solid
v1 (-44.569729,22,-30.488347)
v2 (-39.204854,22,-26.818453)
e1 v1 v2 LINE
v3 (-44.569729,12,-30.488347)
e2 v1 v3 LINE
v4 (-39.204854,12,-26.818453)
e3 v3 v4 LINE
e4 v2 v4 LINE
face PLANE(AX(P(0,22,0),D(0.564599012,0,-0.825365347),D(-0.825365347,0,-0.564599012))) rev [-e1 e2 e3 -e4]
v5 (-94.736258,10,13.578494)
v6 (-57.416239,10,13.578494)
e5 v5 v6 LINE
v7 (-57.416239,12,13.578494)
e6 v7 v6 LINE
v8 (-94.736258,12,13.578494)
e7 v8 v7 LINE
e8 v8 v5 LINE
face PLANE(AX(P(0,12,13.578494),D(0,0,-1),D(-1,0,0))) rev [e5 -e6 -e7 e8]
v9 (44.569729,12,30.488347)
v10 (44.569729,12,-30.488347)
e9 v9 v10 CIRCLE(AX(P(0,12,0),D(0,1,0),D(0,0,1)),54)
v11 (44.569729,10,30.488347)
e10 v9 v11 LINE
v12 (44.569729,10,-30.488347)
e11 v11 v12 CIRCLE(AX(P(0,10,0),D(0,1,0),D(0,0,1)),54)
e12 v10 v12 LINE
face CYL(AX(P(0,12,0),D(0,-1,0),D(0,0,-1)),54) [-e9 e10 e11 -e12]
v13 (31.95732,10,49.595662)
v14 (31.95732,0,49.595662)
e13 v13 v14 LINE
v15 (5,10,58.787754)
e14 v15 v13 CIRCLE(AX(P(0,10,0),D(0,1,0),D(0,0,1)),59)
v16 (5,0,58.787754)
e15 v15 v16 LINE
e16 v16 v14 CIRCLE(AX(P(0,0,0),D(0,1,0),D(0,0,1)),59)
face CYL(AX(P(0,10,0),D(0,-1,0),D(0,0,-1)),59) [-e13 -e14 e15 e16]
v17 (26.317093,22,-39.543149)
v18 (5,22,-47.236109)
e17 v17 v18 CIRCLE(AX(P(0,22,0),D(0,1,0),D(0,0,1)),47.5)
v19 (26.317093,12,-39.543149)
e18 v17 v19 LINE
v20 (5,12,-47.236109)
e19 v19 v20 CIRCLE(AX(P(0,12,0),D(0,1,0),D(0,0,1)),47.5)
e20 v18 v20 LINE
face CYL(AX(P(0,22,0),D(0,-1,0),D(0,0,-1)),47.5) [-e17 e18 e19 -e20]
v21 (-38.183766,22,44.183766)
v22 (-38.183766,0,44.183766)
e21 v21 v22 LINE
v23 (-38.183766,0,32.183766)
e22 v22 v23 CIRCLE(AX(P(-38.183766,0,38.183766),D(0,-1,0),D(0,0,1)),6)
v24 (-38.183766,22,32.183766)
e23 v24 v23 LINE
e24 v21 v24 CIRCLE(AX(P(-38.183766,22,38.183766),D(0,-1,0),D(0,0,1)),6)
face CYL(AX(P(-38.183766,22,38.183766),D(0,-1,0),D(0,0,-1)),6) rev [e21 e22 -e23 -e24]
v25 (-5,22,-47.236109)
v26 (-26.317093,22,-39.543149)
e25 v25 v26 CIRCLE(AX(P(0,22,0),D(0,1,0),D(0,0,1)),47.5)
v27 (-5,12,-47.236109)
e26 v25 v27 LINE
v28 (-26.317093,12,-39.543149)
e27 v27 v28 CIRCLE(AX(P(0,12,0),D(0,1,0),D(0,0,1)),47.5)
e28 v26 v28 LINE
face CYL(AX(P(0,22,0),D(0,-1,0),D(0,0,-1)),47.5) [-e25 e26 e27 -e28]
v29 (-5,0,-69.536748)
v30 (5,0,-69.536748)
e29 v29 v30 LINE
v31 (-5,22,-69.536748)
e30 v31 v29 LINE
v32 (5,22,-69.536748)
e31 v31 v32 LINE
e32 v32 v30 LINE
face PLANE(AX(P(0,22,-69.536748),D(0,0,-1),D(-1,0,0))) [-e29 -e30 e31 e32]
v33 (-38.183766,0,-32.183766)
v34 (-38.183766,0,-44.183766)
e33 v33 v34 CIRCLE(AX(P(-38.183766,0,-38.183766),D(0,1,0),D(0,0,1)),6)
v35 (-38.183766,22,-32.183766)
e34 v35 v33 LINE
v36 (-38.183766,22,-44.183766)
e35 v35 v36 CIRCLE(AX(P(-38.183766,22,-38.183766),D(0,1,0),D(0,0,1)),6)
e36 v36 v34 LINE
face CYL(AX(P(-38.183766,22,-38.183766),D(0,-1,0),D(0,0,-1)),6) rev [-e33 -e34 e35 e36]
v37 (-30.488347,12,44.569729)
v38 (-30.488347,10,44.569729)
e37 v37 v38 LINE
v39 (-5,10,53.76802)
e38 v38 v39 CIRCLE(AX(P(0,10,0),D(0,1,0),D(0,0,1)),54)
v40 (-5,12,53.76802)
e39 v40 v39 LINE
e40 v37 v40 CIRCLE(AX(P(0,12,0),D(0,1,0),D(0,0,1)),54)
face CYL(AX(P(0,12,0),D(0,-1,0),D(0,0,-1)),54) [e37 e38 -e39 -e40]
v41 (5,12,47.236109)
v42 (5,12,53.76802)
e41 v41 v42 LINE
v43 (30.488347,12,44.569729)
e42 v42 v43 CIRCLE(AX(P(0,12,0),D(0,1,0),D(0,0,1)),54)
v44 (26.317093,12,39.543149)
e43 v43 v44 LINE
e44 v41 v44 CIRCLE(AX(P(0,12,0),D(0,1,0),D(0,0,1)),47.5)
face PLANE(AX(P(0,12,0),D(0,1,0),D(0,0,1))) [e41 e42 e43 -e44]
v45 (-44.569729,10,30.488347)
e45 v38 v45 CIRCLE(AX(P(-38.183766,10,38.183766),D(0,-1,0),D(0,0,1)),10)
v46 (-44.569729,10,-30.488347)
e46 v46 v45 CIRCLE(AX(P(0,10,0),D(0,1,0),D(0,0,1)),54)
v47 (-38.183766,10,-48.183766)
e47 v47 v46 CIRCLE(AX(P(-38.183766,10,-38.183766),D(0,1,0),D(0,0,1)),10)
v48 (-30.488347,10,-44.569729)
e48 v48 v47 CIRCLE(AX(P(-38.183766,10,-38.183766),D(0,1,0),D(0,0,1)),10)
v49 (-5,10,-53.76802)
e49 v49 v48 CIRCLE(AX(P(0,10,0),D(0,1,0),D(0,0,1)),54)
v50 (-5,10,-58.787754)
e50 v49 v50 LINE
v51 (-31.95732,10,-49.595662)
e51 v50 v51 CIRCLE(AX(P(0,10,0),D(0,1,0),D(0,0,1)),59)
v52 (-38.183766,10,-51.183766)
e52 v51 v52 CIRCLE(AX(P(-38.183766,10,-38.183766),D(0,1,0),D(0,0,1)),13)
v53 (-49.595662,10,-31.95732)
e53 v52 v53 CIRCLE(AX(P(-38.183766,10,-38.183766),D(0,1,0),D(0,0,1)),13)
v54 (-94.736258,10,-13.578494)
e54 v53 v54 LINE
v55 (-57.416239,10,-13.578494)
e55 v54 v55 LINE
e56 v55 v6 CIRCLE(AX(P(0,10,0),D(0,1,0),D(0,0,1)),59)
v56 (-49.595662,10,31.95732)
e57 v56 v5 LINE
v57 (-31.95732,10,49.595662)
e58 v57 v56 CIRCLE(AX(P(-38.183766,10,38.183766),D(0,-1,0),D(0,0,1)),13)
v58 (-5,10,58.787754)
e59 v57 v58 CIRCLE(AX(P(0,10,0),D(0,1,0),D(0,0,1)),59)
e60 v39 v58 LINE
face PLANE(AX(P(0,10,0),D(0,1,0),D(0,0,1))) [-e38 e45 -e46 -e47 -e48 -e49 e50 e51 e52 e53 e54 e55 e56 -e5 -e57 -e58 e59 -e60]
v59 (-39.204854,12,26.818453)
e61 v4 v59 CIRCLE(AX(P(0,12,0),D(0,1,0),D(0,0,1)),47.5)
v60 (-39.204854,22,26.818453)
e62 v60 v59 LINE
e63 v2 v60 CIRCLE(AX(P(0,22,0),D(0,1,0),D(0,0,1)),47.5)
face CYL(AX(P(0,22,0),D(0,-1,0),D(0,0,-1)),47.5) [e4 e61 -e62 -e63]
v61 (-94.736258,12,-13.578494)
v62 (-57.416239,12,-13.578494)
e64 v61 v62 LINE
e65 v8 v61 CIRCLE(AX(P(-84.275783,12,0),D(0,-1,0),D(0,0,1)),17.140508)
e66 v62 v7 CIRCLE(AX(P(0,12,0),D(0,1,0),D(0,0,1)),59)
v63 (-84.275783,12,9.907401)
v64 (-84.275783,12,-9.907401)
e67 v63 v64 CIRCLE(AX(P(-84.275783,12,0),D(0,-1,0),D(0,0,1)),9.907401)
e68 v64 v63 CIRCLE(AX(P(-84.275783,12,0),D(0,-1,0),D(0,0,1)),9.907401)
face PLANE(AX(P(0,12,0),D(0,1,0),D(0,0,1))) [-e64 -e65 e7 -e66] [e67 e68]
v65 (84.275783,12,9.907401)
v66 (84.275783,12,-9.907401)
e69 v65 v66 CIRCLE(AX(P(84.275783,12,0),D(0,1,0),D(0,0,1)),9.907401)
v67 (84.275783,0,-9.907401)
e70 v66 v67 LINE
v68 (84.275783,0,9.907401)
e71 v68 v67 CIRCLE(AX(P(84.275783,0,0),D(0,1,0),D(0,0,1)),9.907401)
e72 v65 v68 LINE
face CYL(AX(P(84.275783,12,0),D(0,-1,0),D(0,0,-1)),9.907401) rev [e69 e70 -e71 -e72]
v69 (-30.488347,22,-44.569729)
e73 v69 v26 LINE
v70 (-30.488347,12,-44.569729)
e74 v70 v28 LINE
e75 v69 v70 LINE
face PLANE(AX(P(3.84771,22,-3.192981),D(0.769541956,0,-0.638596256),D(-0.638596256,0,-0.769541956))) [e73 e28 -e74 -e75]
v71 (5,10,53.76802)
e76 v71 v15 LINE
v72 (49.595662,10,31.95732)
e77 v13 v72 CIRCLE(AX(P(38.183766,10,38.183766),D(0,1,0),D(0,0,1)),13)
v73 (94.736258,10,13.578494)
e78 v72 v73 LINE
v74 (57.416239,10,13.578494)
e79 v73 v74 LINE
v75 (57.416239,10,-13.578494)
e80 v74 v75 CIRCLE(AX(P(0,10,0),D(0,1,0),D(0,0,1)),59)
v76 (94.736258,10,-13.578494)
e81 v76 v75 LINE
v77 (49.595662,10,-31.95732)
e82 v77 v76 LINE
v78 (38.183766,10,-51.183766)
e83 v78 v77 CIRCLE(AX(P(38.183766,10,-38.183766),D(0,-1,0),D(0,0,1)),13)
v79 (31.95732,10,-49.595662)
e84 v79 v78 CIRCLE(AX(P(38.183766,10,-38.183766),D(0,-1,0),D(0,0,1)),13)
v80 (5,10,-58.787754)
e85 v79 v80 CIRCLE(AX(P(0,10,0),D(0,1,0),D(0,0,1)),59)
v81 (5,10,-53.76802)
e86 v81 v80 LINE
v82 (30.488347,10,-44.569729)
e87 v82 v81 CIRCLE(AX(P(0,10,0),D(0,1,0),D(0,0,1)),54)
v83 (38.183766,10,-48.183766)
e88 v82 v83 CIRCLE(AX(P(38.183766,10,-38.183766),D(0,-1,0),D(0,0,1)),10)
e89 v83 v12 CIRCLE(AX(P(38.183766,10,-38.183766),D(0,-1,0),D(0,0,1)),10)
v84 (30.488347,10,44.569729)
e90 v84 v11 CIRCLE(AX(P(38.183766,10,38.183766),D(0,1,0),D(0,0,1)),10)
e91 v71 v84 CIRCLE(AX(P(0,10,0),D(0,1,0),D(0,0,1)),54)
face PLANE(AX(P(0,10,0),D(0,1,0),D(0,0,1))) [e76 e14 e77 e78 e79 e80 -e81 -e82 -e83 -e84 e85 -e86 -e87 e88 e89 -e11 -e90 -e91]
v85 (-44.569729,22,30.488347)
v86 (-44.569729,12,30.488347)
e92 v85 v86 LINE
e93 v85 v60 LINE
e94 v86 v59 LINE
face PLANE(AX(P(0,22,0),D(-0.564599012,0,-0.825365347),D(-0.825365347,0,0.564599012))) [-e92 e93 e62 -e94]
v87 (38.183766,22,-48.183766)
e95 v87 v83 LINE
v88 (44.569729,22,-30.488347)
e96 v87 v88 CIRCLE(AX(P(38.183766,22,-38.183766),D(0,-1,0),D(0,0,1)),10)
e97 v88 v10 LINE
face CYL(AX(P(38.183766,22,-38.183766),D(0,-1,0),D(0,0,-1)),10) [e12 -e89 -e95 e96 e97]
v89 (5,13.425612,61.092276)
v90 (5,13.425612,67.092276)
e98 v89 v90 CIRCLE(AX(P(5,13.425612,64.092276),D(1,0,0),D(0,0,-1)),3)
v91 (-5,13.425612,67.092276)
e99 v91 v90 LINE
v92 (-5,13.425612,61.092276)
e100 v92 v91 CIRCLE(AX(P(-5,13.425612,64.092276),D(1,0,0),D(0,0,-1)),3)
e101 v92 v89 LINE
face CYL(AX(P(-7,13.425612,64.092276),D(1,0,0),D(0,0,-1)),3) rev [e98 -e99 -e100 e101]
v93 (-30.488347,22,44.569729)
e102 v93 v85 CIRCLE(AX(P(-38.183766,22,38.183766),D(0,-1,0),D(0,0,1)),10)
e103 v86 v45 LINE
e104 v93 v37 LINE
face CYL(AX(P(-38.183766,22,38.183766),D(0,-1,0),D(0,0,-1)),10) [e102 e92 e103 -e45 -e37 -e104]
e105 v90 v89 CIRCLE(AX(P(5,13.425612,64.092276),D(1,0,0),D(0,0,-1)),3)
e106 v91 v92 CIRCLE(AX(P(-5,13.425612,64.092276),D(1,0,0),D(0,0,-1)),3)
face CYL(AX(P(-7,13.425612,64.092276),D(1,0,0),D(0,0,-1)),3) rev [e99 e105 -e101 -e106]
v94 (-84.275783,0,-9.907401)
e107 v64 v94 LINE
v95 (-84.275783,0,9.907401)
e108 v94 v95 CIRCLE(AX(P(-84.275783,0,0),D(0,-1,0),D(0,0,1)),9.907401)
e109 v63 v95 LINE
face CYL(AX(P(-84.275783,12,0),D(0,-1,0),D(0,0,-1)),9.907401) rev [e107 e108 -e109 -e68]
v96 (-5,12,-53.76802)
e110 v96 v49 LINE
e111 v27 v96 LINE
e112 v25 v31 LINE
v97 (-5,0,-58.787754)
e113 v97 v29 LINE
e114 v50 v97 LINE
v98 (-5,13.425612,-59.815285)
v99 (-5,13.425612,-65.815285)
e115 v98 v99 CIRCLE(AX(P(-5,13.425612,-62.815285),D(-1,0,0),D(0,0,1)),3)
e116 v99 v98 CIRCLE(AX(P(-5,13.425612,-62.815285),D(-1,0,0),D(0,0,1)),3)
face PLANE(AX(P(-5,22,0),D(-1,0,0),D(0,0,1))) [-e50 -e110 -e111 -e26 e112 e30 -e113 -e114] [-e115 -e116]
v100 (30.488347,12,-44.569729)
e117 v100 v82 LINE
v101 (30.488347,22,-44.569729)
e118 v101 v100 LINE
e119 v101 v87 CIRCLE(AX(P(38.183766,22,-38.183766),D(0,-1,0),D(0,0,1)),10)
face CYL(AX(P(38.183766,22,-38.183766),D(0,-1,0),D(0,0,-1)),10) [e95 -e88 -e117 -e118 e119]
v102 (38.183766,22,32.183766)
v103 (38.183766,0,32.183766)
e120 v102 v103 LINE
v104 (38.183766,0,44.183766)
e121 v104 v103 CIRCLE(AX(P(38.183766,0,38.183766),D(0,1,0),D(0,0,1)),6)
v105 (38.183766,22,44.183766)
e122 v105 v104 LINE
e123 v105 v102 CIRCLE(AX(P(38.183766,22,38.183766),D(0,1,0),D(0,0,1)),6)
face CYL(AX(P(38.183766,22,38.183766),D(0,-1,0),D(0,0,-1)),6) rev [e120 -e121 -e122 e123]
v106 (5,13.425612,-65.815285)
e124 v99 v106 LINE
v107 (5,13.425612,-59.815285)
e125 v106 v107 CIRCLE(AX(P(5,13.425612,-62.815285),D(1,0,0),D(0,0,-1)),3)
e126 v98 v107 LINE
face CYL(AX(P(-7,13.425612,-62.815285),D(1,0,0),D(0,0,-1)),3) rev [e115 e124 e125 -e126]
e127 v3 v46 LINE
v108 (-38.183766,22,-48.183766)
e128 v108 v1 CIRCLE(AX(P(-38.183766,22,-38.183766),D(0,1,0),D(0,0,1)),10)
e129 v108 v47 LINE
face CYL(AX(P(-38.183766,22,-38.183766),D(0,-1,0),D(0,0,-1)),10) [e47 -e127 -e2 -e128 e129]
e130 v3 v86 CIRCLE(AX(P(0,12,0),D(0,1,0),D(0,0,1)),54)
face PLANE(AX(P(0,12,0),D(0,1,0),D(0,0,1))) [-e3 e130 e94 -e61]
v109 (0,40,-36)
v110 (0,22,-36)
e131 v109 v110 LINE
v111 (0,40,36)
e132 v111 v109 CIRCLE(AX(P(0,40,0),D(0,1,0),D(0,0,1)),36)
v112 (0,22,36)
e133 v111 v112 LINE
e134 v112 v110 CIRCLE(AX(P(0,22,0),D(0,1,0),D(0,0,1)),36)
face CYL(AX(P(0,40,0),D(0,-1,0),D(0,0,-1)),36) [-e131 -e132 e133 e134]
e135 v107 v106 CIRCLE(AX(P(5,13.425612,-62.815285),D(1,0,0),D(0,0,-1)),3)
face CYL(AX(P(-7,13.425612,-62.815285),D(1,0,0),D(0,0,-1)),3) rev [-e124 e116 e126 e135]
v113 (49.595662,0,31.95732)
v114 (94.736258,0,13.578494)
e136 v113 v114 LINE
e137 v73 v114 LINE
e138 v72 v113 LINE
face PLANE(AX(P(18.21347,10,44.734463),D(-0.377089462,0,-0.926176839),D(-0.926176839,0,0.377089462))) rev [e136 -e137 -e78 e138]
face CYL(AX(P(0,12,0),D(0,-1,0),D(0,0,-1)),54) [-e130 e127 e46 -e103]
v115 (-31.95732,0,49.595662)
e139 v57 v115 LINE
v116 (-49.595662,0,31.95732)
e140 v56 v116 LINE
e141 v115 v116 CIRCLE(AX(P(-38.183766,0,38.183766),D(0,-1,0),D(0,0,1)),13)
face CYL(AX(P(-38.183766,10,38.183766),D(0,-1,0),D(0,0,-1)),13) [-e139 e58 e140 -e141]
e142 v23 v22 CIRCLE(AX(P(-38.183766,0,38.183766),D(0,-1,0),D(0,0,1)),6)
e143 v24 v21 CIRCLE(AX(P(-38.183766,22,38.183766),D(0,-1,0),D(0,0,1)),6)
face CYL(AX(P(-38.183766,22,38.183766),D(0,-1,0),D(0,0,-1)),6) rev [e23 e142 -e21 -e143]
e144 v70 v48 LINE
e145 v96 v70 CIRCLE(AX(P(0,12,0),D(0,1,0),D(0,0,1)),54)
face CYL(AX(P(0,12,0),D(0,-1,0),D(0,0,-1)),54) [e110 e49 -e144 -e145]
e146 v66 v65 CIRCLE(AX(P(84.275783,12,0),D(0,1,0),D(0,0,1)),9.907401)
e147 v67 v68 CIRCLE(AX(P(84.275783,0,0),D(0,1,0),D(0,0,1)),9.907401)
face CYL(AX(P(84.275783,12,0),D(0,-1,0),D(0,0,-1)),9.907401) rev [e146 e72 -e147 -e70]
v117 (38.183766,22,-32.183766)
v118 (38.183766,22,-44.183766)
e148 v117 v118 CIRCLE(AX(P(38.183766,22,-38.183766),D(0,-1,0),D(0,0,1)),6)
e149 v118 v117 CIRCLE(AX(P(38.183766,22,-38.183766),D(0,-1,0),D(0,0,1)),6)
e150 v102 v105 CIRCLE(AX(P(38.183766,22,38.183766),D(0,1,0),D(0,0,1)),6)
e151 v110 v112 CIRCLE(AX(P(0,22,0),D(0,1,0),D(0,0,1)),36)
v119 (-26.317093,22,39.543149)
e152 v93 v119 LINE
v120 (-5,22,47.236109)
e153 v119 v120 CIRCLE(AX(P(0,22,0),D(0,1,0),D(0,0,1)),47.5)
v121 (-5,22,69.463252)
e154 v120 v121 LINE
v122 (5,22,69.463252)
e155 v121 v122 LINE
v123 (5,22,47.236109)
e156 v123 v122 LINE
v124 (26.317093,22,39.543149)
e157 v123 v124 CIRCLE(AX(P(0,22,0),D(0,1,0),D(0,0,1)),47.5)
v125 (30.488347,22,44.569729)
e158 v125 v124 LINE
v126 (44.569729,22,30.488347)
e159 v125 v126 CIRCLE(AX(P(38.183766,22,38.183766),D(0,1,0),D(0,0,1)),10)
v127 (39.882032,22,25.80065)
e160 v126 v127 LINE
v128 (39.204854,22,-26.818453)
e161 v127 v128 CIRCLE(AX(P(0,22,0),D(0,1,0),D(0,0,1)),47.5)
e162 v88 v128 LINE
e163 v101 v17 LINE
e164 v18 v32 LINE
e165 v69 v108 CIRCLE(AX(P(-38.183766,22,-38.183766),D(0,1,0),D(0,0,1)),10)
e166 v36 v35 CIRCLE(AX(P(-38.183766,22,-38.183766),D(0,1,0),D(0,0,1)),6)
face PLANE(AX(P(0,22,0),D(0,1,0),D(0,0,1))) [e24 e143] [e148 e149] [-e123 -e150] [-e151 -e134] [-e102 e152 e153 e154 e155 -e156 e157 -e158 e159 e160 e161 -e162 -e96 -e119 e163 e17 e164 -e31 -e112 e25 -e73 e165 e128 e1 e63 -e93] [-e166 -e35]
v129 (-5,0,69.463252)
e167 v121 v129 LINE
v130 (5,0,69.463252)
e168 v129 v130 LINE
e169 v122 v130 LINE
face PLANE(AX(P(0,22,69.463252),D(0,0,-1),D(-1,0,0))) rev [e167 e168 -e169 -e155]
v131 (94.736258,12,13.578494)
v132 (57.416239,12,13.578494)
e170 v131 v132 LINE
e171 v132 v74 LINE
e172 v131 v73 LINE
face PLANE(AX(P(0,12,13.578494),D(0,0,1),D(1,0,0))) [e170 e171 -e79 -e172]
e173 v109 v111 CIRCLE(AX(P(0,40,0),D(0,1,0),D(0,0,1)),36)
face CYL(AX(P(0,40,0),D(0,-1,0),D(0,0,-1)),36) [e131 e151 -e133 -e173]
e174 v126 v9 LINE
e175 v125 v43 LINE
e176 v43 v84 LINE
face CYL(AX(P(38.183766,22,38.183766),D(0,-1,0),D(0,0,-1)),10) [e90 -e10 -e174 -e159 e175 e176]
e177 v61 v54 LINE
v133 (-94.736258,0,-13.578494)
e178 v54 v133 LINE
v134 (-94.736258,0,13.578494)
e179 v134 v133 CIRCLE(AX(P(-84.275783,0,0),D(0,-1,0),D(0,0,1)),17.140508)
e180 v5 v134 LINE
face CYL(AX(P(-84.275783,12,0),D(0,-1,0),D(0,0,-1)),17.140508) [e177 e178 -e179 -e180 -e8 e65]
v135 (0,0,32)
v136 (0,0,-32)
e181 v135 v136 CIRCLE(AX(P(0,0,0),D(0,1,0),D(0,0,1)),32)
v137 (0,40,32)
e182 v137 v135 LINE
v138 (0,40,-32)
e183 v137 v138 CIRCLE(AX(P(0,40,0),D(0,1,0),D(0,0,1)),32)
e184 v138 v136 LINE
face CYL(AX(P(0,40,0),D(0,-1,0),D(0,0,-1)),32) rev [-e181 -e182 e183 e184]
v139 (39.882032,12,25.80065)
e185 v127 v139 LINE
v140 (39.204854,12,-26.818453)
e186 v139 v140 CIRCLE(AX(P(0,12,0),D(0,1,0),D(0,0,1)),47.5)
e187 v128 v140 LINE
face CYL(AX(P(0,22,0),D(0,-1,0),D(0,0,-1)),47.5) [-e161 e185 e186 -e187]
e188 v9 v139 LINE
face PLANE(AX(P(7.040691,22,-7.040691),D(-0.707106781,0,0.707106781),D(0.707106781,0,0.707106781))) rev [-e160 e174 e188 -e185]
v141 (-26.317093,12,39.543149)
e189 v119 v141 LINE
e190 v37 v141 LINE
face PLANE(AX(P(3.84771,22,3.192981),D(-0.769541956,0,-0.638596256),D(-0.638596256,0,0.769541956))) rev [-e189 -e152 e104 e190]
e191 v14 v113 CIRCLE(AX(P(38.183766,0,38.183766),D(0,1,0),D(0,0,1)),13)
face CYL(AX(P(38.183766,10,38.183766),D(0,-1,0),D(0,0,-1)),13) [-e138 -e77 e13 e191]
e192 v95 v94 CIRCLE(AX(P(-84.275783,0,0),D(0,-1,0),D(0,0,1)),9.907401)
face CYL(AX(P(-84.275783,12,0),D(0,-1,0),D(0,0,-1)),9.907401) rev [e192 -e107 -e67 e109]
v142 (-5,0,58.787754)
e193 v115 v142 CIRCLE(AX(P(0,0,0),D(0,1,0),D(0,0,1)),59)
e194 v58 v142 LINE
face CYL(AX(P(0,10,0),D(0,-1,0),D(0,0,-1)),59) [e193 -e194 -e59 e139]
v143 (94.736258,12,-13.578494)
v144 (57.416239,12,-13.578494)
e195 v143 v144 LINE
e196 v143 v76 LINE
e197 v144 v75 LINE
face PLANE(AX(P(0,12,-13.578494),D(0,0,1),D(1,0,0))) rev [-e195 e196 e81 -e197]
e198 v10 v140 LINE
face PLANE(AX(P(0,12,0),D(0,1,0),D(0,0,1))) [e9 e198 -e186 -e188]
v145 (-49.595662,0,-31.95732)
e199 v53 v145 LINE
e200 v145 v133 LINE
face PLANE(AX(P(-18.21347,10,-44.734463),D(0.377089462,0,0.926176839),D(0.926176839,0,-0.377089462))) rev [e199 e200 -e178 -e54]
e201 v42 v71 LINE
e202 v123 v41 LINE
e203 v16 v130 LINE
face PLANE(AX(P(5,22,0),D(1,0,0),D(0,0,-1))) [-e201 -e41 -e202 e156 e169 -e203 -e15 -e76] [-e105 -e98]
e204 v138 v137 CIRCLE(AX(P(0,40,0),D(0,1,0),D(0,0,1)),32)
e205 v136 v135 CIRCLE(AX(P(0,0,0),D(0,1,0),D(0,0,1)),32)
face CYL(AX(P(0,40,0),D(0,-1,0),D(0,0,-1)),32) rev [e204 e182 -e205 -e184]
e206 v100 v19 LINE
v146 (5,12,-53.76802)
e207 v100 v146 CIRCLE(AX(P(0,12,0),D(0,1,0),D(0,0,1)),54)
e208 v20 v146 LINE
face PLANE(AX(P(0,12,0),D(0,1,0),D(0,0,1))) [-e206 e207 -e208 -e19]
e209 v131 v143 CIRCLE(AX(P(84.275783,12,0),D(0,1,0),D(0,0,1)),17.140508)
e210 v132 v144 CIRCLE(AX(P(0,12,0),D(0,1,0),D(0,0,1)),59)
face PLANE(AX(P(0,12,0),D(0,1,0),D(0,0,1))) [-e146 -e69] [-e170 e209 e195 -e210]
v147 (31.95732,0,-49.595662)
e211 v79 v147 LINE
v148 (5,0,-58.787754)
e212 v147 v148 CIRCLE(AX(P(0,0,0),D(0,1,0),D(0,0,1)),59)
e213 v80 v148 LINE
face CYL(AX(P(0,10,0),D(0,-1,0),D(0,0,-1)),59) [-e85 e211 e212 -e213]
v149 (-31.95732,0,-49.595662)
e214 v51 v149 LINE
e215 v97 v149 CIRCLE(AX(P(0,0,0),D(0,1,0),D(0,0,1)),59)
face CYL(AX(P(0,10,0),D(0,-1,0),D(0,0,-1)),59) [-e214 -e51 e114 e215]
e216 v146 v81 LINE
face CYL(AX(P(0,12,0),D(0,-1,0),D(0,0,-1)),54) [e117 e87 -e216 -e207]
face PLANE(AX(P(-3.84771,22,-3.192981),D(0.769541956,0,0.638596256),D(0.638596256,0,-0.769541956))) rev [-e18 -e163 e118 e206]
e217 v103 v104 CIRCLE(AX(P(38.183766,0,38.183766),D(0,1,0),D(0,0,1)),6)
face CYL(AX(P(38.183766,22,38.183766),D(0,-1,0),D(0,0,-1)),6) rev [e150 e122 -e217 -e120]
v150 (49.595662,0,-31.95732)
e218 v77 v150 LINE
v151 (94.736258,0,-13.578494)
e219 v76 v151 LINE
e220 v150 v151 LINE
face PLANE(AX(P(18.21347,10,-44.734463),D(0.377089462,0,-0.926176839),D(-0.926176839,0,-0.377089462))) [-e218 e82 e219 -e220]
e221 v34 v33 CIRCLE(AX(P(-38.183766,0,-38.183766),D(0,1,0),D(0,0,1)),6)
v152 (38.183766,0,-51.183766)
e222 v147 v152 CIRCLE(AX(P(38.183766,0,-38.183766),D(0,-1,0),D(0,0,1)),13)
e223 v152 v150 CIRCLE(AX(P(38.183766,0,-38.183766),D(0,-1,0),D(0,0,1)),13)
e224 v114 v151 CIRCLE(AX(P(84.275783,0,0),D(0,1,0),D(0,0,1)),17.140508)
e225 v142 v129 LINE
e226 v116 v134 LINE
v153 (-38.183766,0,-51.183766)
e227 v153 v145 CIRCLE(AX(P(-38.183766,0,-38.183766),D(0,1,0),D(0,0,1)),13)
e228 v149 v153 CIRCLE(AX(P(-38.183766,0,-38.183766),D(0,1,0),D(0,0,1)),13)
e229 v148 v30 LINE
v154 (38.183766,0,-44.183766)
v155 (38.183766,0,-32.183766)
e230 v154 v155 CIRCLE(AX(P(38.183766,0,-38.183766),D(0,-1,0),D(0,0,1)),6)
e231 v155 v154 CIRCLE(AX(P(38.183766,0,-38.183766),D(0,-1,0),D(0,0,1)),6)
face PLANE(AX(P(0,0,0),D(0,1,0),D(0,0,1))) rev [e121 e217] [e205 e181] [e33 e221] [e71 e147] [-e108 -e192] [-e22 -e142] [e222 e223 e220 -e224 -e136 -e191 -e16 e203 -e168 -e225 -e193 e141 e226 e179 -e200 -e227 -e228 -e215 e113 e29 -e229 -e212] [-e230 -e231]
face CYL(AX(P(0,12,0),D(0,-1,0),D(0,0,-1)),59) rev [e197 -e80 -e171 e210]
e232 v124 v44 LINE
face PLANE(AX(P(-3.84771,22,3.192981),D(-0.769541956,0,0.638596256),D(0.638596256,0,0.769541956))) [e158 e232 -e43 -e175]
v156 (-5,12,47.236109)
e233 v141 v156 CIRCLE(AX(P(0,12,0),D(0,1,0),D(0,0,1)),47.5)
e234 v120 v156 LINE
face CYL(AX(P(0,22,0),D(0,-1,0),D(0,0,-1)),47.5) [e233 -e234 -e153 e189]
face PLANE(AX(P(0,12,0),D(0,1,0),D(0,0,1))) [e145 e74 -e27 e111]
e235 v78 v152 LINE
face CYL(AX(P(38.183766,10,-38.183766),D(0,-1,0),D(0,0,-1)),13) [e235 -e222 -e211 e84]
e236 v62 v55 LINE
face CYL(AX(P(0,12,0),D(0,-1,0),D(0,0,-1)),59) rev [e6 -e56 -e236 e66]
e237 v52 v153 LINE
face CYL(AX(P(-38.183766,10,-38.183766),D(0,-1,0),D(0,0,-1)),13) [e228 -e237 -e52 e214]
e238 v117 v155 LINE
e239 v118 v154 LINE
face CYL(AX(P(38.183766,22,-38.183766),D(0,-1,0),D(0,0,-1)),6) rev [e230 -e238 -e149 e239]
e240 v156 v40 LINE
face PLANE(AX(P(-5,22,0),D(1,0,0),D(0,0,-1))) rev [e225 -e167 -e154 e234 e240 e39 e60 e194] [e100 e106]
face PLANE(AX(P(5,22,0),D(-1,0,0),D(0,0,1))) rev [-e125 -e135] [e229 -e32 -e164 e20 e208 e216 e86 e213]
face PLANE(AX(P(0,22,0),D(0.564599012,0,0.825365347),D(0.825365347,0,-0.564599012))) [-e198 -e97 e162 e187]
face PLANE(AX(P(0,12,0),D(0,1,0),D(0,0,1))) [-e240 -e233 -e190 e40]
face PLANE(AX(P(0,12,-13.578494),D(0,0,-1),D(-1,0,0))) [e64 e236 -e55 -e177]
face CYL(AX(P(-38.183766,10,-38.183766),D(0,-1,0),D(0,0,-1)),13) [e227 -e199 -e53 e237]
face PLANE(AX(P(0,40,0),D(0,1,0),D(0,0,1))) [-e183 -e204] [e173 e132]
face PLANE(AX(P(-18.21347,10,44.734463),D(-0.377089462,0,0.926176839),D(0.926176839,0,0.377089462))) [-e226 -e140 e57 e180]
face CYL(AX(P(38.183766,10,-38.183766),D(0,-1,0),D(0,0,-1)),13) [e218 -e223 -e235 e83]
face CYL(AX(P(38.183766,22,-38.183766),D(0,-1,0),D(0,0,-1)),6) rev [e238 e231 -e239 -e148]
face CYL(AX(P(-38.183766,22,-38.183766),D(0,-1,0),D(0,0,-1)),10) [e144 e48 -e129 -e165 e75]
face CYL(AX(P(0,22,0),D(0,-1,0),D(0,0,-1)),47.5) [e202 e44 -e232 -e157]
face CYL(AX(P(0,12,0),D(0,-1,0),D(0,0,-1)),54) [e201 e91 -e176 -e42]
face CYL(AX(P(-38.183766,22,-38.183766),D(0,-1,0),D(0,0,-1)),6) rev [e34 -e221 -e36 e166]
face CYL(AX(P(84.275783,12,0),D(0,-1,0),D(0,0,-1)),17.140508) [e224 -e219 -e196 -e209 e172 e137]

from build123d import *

# Parameters (mm, degrees)
HOUSING_LAYOUT_SKETCH_R   = 36
HOUSING_LAYOUT_SKETCH_R_2 = 32
HOUSING_BODY_H40_DEPTH    = 40
SKETCH1_7_R               = 36
RAISED_BOSS_H22_1_DEPTH   = 22
RAISED_BOSS_H12_1_DEPTH   = 12
RAISED_BOSS_H10_1_DEPTH   = 10
RAISED_BOSS_H22_2_DEPTH   = 22
RAISED_BOSS_H12_2_DEPTH   = 12
RAISED_BOSS_H10_2_DEPTH   = 10
RAISED_BOSS_H22_3_DEPTH   = 22
RAISED_BOSS_H10_3_DEPTH   = 10
RAISED_BOSS_H22_4_DEPTH   = 22
RAISED_BOSS_H10_4_DEPTH   = 10
SKETCH1_21_R              = 9.907401239
RAISED_BOSS_H12_3_DEPTH   = 12
BOSS_CUT_SKETCH_R         = 3
BOSS_CUT_D12_DEPTH        = 12


with BuildPart() as part:
    # Housing Layout Sketch → Housing Body H40 (new body)
    with BuildSketch(Plane(origin=(0, 0, 0), x_dir=(1, 0, 0), z_dir=(0, 1, 0))):
        with Locations(Location((0, 0, 0), (0, 0, 270))):
            Circle(HOUSING_LAYOUT_SKETCH_R)
        with Locations(Location((0, 0, 0), (0, 0, 270))):
            Circle(HOUSING_LAYOUT_SKETCH_R_2, mode=Mode.SUBTRACT)
    extrude(amount=HOUSING_BODY_H40_DEPTH)

    # Sketch1_7 → Raised Boss H22 1 (add)
    with BuildSketch(Plane(origin=(0, 0, 0), x_dir=(1, 0, 0), z_dir=(0, 1, 0))):
        with BuildLine():
            ThreePointArc((-5, 47.236109069), (-20.465112279, 42.865244423), (-33.587572106, 33.587572106))
            ThreePointArc((-33.587572106, 33.587572106), (-44.781324678, -15.839285339), (-5, -47.236109069))
            Line((-5, -47.236109069), (-5, -53.768020235))
            ThreePointArc((-5, -53.768020235), (0, -54), (5, -53.768020235))
            Line((5, -53.768020235), (5, -47.236109069))
            ThreePointArc((5, -47.236109069), (47.5, 0), (5, 47.236109069))
            Line((5, 47.236109069), (5, 53.768020235))
            ThreePointArc((5, 53.768020235), (0, 54), (-5, 53.768020235))
            Line((-5, 53.768020235), (-5, 47.236109069))
        make_face()
        with Locations(Location((0, 0, 0), (0, 0, 270))):
            Circle(SKETCH1_7_R, mode=Mode.SUBTRACT)
    extrude(amount=RAISED_BOSS_H22_1_DEPTH)

    # Sketch1_9 → Raised Boss H12 1 (add)
    with BuildSketch(Plane(origin=(0, 0, 0), x_dir=(1, 0, 0), z_dir=(0, 1, 0))):
        with BuildLine():
            ThreePointArc((-39.204853986, -26.818453049), (-47.5, 0), (-39.204853986, 26.818453049))
            Line((-39.204853986, 26.818453049), (-44.569728742, 30.488346624))
            ThreePointArc((-44.569728742, 30.488346624), (-54, 0), (-44.569728742, -30.488346624))
            Line((-44.569728742, -30.488346624), (-39.204853986, -26.818453049))
        make_face()
        with BuildLine():
            Line((44.569728742, 30.488346624), (39.204853986, 26.818453049))
            ThreePointArc((39.204853986, 26.818453049), (47.49606696, 0.611247373), (39.882031918, -25.8006498))
            Line((39.882031918, -25.8006498), (44.569728742, -30.488346624))
            ThreePointArc((44.569728742, -30.488346624), (54, 0), (44.569728742, 30.488346624))
        make_face()
    extrude(amount=RAISED_BOSS_H12_1_DEPTH)

    # Sketch1_10 → Raised Boss H10 1 (add)
    with BuildSketch(Plane(origin=(0, 0, 0), x_dir=(1, 0, 0), z_dir=(0, 1, 0))):
        with BuildLine():
            ThreePointArc((-44.569728742, -30.488346624), (-54, 0), (-44.569728742, 30.488346624))
            ThreePointArc((-44.569728742, 30.488346624), (-46.384787995, 32.461595157), (-47.610345509, 34.846161919))
            ThreePointArc((-47.610345509, 34.846161919), (-59, 0), (-47.610345509, -34.846161919))
            ThreePointArc((-47.610345509, -34.846161919), (-46.384787995, -32.461595157), (-44.569728742, -30.488346624))
        make_face()
        with BuildLine():
            ThreePointArc((47.610345509, -34.846161919), (59, 0), (47.610345509, 34.846161919))
            ThreePointArc((47.610345509, 34.846161919), (46.384787995, 32.461595157), (44.569728742, 30.488346624))
            ThreePointArc((44.569728742, 30.488346624), (54, 0), (44.569728742, -30.488346624))
            ThreePointArc((44.569728742, -30.488346624), (46.384787995, -32.461595157), (47.610345509, -34.846161919))
        make_face()
    extrude(amount=RAISED_BOSS_H10_1_DEPTH)

    # Sketch1_11 → Raised Boss H22 2 (add)
    with BuildSketch(Plane(origin=(0, 0, 0), x_dir=(1, 0, 0), z_dir=(0, 1, 0))):
        with BuildLine():
            ThreePointArc((5, -58.787753827), (0, -59), (-5, -58.787753827))
            Line((-5, -58.787753827), (-5, -69.463251536))
            Line((-5, -69.463251536), (5, -69.463251536))
            Line((5, -69.463251536), (5, -58.787753827))
        make_face()
        with BuildLine():
            Line((-5, 69.536748464), (-5, 58.787753827))
            ThreePointArc((-5, 58.787753827), (0, 59), (5, 58.787753827))
            Line((5, 58.787753827), (5, 69.536748464))
            Line((5, 69.536748464), (-5, 69.536748464))
        make_face()
        with BuildLine():
            Line((-5, 58.787753827), (-5, 53.768020235))
            ThreePointArc((-5, 53.768020235), (0, 54), (5, 53.768020235))
            Line((5, 53.768020235), (5, 58.787753827))
            ThreePointArc((5, 58.787753827), (0, 59), (-5, 58.787753827))
        make_face()
        with BuildLine():
            ThreePointArc((5, -53.768020235), (0, -54), (-5, -53.768020235))
            Line((-5, -53.768020235), (-5, -58.787753827))
            ThreePointArc((-5, -58.787753827), (0, -59), (5, -58.787753827))
            Line((5, -58.787753827), (5, -53.768020235))
        make_face()
    extrude(amount=RAISED_BOSS_H22_2_DEPTH)

    # Sketch1_14 → Raised Boss H12 2 (add)
    with BuildSketch(Plane(origin=(0, 0, 0), x_dir=(1, 0, 0), z_dir=(0, 1, 0))):
        with BuildLine():
            ThreePointArc((-5, -47.236109069), (-16.124065271, -44.679576085), (-26.31709261, -39.543149047))
            Line((-26.31709261, -39.543149047), (-30.488346624, -44.569728742))
            ThreePointArc((-30.488346624, -44.569728742), (-18.330516308, -50.793623339), (-5, -53.768020235))
            Line((-5, -53.768020235), (-5, -47.236109069))
        make_face()
        with BuildLine():
            Line((5, -47.236109069), (5, -53.768020235))
            ThreePointArc((5, -53.768020235), (18.330516308, -50.793623339), (30.488346624, -44.569728742))
            Line((30.488346624, -44.569728742), (26.31709261, -39.543149047))
            ThreePointArc((26.31709261, -39.543149047), (16.124065271, -44.679576085), (5, -47.236109069))
        make_face()
        with BuildLine():
            ThreePointArc((30.488346624, 44.569728742), (18.330516308, 50.793623339), (5, 53.768020235))
            Line((5, 53.768020235), (5, 47.236109069))
            ThreePointArc((5, 47.236109069), (16.124065271, 44.679576085), (26.31709261, 39.543149047))
            Line((26.31709261, 39.543149047), (30.488346624, 44.569728742))
        make_face()
        with BuildLine():
            Line((-30.488346624, 44.569728742), (-26.31709261, 39.543149047))
            ThreePointArc((-26.31709261, 39.543149047), (-16.124065271, 44.679576085), (-5, 47.236109069))
            Line((-5, 47.236109069), (-5, 53.768020235))
            ThreePointArc((-5, 53.768020235), (-18.330516308, 50.793623339), (-30.488346624, 44.569728742))
        make_face()
    extrude(amount=RAISED_BOSS_H12_2_DEPTH)

    # Sketch1_15 → Raised Boss H10 2 (add)
    with BuildSketch(Plane(origin=(0, 0, 0), x_dir=(1, 0, 0), z_dir=(0, 1, 0))):
        with BuildLine():
            ThreePointArc((-5, -53.768020235), (-18.330516308, -50.793623339), (-30.488346624, -44.569728742))
            ThreePointArc((-30.488346624, -44.569728742), (-32.461595157, -46.384787995), (-34.846161919, -47.610345509))
            ThreePointArc((-34.846161919, -47.610345509), (-33.416487996, -48.624462259), (-31.957320012, -49.595662085))
            ThreePointArc((-31.957320012, -49.595662085), (-19.041652062, -55.842774705), (-5, -58.787753827))
            Line((-5, -58.787753827), (-5, -53.768020235))
        make_face()
        with BuildLine():
            ThreePointArc((30.488346624, -44.569728742), (18.330516308, -50.793623339), (5, -53.768020235))
            Line((5, -53.768020235), (5, -58.787753827))
            ThreePointArc((5, -58.787753827), (19.041652062, -55.842774705), (31.957320012, -49.595662085))
            ThreePointArc((31.957320012, -49.595662085), (33.416487996, -48.624462259), (34.846161919, -47.610345509))
            ThreePointArc((34.846161919, -47.610345509), (32.461595157, -46.384787995), (30.488346624, -44.569728742))
        make_face()
        with BuildLine():
            ThreePointArc((-34.846161919, 47.610345509), (-32.461595157, 46.384787995), (-30.488346624, 44.569728742))
            ThreePointArc((-30.488346624, 44.569728742), (-18.330516308, 50.793623339), (-5, 53.768020235))
            Line((-5, 53.768020235), (-5, 58.787753827))
            ThreePointArc((-5, 58.787753827), (-19.041652062, 55.842774705), (-31.957320012, 49.595662085))
            ThreePointArc((-31.957320012, 49.595662085), (-33.416487996, 48.624462259), (-34.846161919, 47.610345509))
        make_face()
        with BuildLine():
            Line((5, 58.787753827), (5, 53.768020235))
            ThreePointArc((5, 53.768020235), (18.330516308, 50.793623339), (30.488346624, 44.569728742))
            ThreePointArc((30.488346624, 44.569728742), (32.461595157, 46.384787995), (34.846161919, 47.610345509))
            ThreePointArc((34.846161919, 47.610345509), (33.416487996, 48.624462259), (31.957320012, 49.595662085))
            ThreePointArc((31.957320012, 49.595662085), (19.041652062, 55.842774705), (5, 58.787753827))
        make_face()
    extrude(amount=RAISED_BOSS_H10_2_DEPTH)

    # Sketch1_16 → Raised Boss H22 3 (add)
    with BuildSketch(Plane(origin=(0, 0, 0), x_dir=(1, 0, 0), z_dir=(0, 1, 0))):
        with BuildLine():
            ThreePointArc((-26.31709261, -39.543149047), (-33.373055651, -33.800727159), (-39.204853986, -26.818453049))
            Line((-39.204853986, -26.818453049), (-44.569728742, -30.488346624))
            ThreePointArc((-44.569728742, -30.488346624), (-43.406876338, -32.122314465), (-42.184152266, -33.711975581))
            ThreePointArc((-42.184152266, -33.711975581), (-35.734512879, -32.706434877), (-32.183766184, -38.183766184))
            ThreePointArc((-32.183766184, -38.183766184), (-32.578824453, -40.324940673), (-33.711975581, -42.184152266))
            ThreePointArc((-33.711975581, -42.184152266), (-32.122314465, -43.406876338), (-30.488346624, -44.569728742))
            Line((-30.488346624, -44.569728742), (-26.31709261, -39.543149047))
        make_face()
        with BuildLine():
            ThreePointArc((-39.204853986, 26.818453049), (-36.553242911, 30.333322151), (-33.587572106, 33.587572106))
            Line((-33.587572106, 33.587572106), (-33.941125497, 33.941125497))
            ThreePointArc((-33.941125497, 33.941125497), (-38.01703513, 32.186083235), (-42.184152266, 33.711975581))
            ThreePointArc((-42.184152266, 33.711975581), (-43.406876338, 32.122314465), (-44.569728742, 30.488346624))
            Line((-44.569728742, 30.488346624), (-39.204853986, 26.818453049))
        make_face()
        with BuildLine():
            Line((-33.941125497, 33.941125497), (-33.587572106, 33.587572106))
            ThreePointArc((-33.587572106, 33.587572106), (-30.099990662, 36.745619632), (-26.31709261, 39.543149047))
            Line((-26.31709261, 39.543149047), (-30.488346624, 44.569728742))
            ThreePointArc((-30.488346624, 44.569728742), (-32.122314465, 43.406876338), (-33.711975581, 42.184152266))
            ThreePointArc((-33.711975581, 42.184152266), (-32.578824453, 40.324940673), (-32.183766184, 38.183766184))
            ThreePointArc((-32.183766184, 38.183766184), (-32.640488989, 35.88766559), (-33.941125497, 33.941125497))
        make_face()
        with BuildLine():
            ThreePointArc((33.711975581, 42.184152266), (32.122314465, 43.406876338), (30.488346624, 44.569728742))
            Line((30.488346624, 44.569728742), (26.31709261, 39.543149047))
            ThreePointArc((26.31709261, 39.543149047), (33.373055651, 33.800727159), (39.204853986, 26.818453049))
            Line((39.204853986, 26.818453049), (44.569728742, 30.488346624))
            ThreePointArc((44.569728742, 30.488346624), (43.406876338, 32.122314465), (42.184152266, 33.711975581))
            ThreePointArc((42.184152266, 33.711975581), (33.941125497, 33.941125497), (33.711975581, 42.184152266))
        make_face()
    extrude(amount=RAISED_BOSS_H22_3_DEPTH)

    # Sketch1_18 → Raised Boss H10 3 (add)
    with BuildSketch(Plane(origin=(0, 0, 0), x_dir=(1, 0, 0), z_dir=(0, 1, 0))):
        with BuildLine():
            ThreePointArc((49.595662085, 31.957320012), (47.376154339, 47.376154339), (31.957320012, 49.595662085))
            ThreePointArc((31.957320012, 49.595662085), (33.416487996, 48.624462259), (34.846161919, 47.610345509))
            ThreePointArc((34.846161919, 47.610345509), (45.254833996, 45.254833996), (47.610345509, 34.846161919))
            ThreePointArc((47.610345509, 34.846161919), (48.624462259, 33.416487996), (49.595662085, 31.957320012))
        make_face()
        with BuildLine():
            ThreePointArc((-47.610345509, 34.846161919), (-45.254833996, 45.254833996), (-34.846161919, 47.610345509))
            ThreePointArc((-34.846161919, 47.610345509), (-33.416487996, 48.624462259), (-31.957320012, 49.595662085))
            ThreePointArc((-31.957320012, 49.595662085), (-47.376154339, 47.376154339), (-49.595662085, 31.957320012))
            ThreePointArc((-49.595662085, 31.957320012), (-48.624462259, 33.416487996), (-47.610345509, 34.846161919))
        make_face()
        with BuildLine():
            ThreePointArc((-34.846161919, -47.610345509), (-45.254833996, -45.254833996), (-47.610345509, -34.846161919))
            ThreePointArc((-47.610345509, -34.846161919), (-48.624462259, -33.416487996), (-49.595662085, -31.957320012))
            ThreePointArc((-49.595662085, -31.957320012), (-47.376154339, -47.376154339), (-31.957320012, -49.595662085))
            ThreePointArc((-31.957320012, -49.595662085), (-33.416487996, -48.624462259), (-34.846161919, -47.610345509))
        make_face()
        with BuildLine():
            ThreePointArc((34.846161919, -47.610345509), (33.416487996, -48.624462259), (31.957320012, -49.595662085))
            ThreePointArc((31.957320012, -49.595662085), (47.376154339, -47.376154339), (49.595662085, -31.957320012))
            ThreePointArc((49.595662085, -31.957320012), (48.624462259, -33.416487996), (47.610345509, -34.846161919))
            ThreePointArc((47.610345509, -34.846161919), (45.254833996, -45.254833996), (34.846161919, -47.610345509))
        make_face()
    extrude(amount=RAISED_BOSS_H10_3_DEPTH)

    # Sketch1_19 → Raised Boss H22 4 (add)
    with BuildSketch(Plane(origin=(0, 0, 0), x_dir=(1, 0, 0), z_dir=(0, 1, 0))):
        with BuildLine():
            ThreePointArc((39.196959086, -44.097600824), (37.063199887, -45.90554666), (34.846161919, -47.610345509))
            ThreePointArc((34.846161919, -47.610345509), (45.254833996, -45.254833996), (47.610345509, -34.846161919))
            ThreePointArc((47.610345509, -34.846161919), (45.90554666, -37.063199887), (44.097600824, -39.196959086))
            ThreePointArc((44.097600824, -39.196959086), (42.426406871, -42.426406871), (39.196959086, -44.097600824))
        make_face()
        with BuildLine():
            Line((26.31709261, -39.543149047), (30.488346624, -44.569728742))
            ThreePointArc((30.488346624, -44.569728742), (32.122314465, -43.406876338), (33.711975581, -42.184152266))
            ThreePointArc((33.711975581, -42.184152266), (33.941125497, -33.941125497), (42.184152266, -33.711975581))
            ThreePointArc((42.184152266, -33.711975581), (43.406876338, -32.122314465), (44.569728742, -30.488346624))
            Line((44.569728742, -30.488346624), (39.882031918, -25.8006498))
            ThreePointArc((39.882031918, -25.8006498), (33.805252454, -33.368471744), (26.31709261, -39.543149047))
        make_face()
        with BuildLine():
            ThreePointArc((33.711975581, -42.184152266), (32.122314465, -43.406876338), (30.488346624, -44.569728742))
            ThreePointArc((30.488346624, -44.569728742), (32.461595157, -46.384787995), (34.846161919, -47.610345509))
            ThreePointArc((34.846161919, -47.610345509), (37.063199887, -45.90554666), (39.196959086, -44.097600824))
            ThreePointArc((39.196959086, -44.097600824), (36.207457539, -43.848940863), (33.711975581, -42.184152266))
        make_face()
        with BuildLine():
            ThreePointArc((47.610345509, -34.846161919), (46.384787995, -32.461595157), (44.569728742, -30.488346624))
            ThreePointArc((44.569728742, -30.488346624), (43.406876338, -32.122314465), (42.184152266, -33.711975581))
            ThreePointArc((42.184152266, -33.711975581), (43.661097491, -35.734512879), (44.183766184, -38.183766184))
            ThreePointArc((44.183766184, -38.183766184), (44.162186035, -38.692191283), (44.097600824, -39.196959086))
            ThreePointArc((44.097600824, -39.196959086), (45.90554666, -37.063199887), (47.610345509, -34.846161919))
        make_face()
        with BuildLine():
            ThreePointArc((33.711975581, -42.184152266), (32.122314465, -43.406876338), (30.488346624, -44.569728742))
            ThreePointArc((30.488346624, -44.569728742), (32.461595157, -46.384787995), (34.846161919, -47.610345509))
            ThreePointArc((34.846161919, -47.610345509), (37.063199887, -45.90554666), (39.196959086, -44.097600824))
            ThreePointArc((39.196959086, -44.097600824), (36.207457539, -43.848940863), (33.711975581, -42.184152266))
        make_face()
        with BuildLine():
            ThreePointArc((47.610345509, -34.846161919), (46.384787995, -32.461595157), (44.569728742, -30.488346624))
            ThreePointArc((44.569728742, -30.488346624), (43.406876338, -32.122314465), (42.184152266, -33.711975581))
            ThreePointArc((42.184152266, -33.711975581), (43.661097491, -35.734512879), (44.183766184, -38.183766184))
            ThreePointArc((44.183766184, -38.183766184), (44.162186035, -38.692191283), (44.097600824, -39.196959086))
            ThreePointArc((44.097600824, -39.196959086), (45.90554666, -37.063199887), (47.610345509, -34.846161919))
        make_face()
        with BuildLine():
            ThreePointArc((-44.097600824, -39.196959086), (-45.90554666, -37.063199887), (-47.610345509, -34.846161919))
            ThreePointArc((-47.610345509, -34.846161919), (-45.254833996, -45.254833996), (-34.846161919, -47.610345509))
            ThreePointArc((-34.846161919, -47.610345509), (-37.063199887, -45.90554666), (-39.196959086, -44.097600824))
            ThreePointArc((-39.196959086, -44.097600824), (-42.426406871, -42.426406871), (-44.097600824, -39.196959086))
        make_face()
        with BuildLine():
            ThreePointArc((-42.184152266, -33.711975581), (-43.406876338, -32.122314465), (-44.569728742, -30.488346624))
            ThreePointArc((-44.569728742, -30.488346624), (-46.384787995, -32.461595157), (-47.610345509, -34.846161919))
            ThreePointArc((-47.610345509, -34.846161919), (-45.90554666, -37.063199887), (-44.097600824, -39.196959086))
            ThreePointArc((-44.097600824, -39.196959086), (-43.848940863, -36.207457539), (-42.184152266, -33.711975581))
        make_face()
        with BuildLine():
            ThreePointArc((-34.846161919, -47.610345509), (-32.461595157, -46.384787995), (-30.488346624, -44.569728742))
            ThreePointArc((-30.488346624, -44.569728742), (-32.122314465, -43.406876338), (-33.711975581, -42.184152266))
            ThreePointArc((-33.711975581, -42.184152266), (-36.207457539, -43.848940863), (-39.196959086, -44.097600824))
            ThreePointArc((-39.196959086, -44.097600824), (-37.063199887, -45.90554666), (-34.846161919, -47.610345509))
        make_face()
        with BuildLine():
            ThreePointArc((-42.184152266, -33.711975581), (-43.406876338, -32.122314465), (-44.569728742, -30.488346624))
            ThreePointArc((-44.569728742, -30.488346624), (-46.384787995, -32.461595157), (-47.610345509, -34.846161919))
            ThreePointArc((-47.610345509, -34.846161919), (-45.90554666, -37.063199887), (-44.097600824, -39.196959086))
            ThreePointArc((-44.097600824, -39.196959086), (-43.848940863, -36.207457539), (-42.184152266, -33.711975581))
        make_face()
        with BuildLine():
            ThreePointArc((-34.846161919, -47.610345509), (-32.461595157, -46.384787995), (-30.488346624, -44.569728742))
            ThreePointArc((-30.488346624, -44.569728742), (-32.122314465, -43.406876338), (-33.711975581, -42.184152266))
            ThreePointArc((-33.711975581, -42.184152266), (-36.207457539, -43.848940863), (-39.196959086, -44.097600824))
            ThreePointArc((-39.196959086, -44.097600824), (-37.063199887, -45.90554666), (-34.846161919, -47.610345509))
        make_face()
        with BuildLine():
            ThreePointArc((34.846161919, 47.610345509), (32.461595157, 46.384787995), (30.488346624, 44.569728742))
            ThreePointArc((30.488346624, 44.569728742), (32.122314465, 43.406876338), (33.711975581, 42.184152266))
            ThreePointArc((33.711975581, 42.184152266), (36.207457539, 43.848940863), (39.196959086, 44.097600824))
            ThreePointArc((39.196959086, 44.097600824), (37.063199887, 45.90554666), (34.846161919, 47.610345509))
        make_face()
        with BuildLine():
            ThreePointArc((44.183766184, 38.183766184), (43.661097491, 35.734512879), (42.184152266, 33.711975581))
            ThreePointArc((42.184152266, 33.711975581), (43.406876338, 32.122314465), (44.569728742, 30.488346624))
            ThreePointArc((44.569728742, 30.488346624), (46.384787995, 32.461595157), (47.610345509, 34.846161919))
            ThreePointArc((47.610345509, 34.846161919), (45.90554666, 37.063199887), (44.097600824, 39.196959086))
            ThreePointArc((44.097600824, 39.196959086), (44.162186035, 38.692191283), (44.183766184, 38.183766184))
        make_face()
        with BuildLine():
            ThreePointArc((34.846161919, 47.610345509), (32.461595157, 46.384787995), (30.488346624, 44.569728742))
            ThreePointArc((30.488346624, 44.569728742), (32.122314465, 43.406876338), (33.711975581, 42.184152266))
            ThreePointArc((33.711975581, 42.184152266), (36.207457539, 43.848940863), (39.196959086, 44.097600824))
            ThreePointArc((39.196959086, 44.097600824), (37.063199887, 45.90554666), (34.846161919, 47.610345509))
        make_face()
        with BuildLine():
            ThreePointArc((44.183766184, 38.183766184), (43.661097491, 35.734512879), (42.184152266, 33.711975581))
            ThreePointArc((42.184152266, 33.711975581), (43.406876338, 32.122314465), (44.569728742, 30.488346624))
            ThreePointArc((44.569728742, 30.488346624), (46.384787995, 32.461595157), (47.610345509, 34.846161919))
            ThreePointArc((47.610345509, 34.846161919), (45.90554666, 37.063199887), (44.097600824, 39.196959086))
            ThreePointArc((44.097600824, 39.196959086), (44.162186035, 38.692191283), (44.183766184, 38.183766184))
        make_face()
        with BuildLine():
            ThreePointArc((47.610345509, 34.846161919), (45.254833996, 45.254833996), (34.846161919, 47.610345509))
            ThreePointArc((34.846161919, 47.610345509), (37.063199887, 45.90554666), (39.196959086, 44.097600824))
            ThreePointArc((39.196959086, 44.097600824), (42.426406871, 42.426406871), (44.097600824, 39.196959086))
            ThreePointArc((44.097600824, 39.196959086), (45.90554666, 37.063199887), (47.610345509, 34.846161919))
        make_face()
        with BuildLine():
            ThreePointArc((-47.610345509, 34.846161919), (-45.90554666, 37.063199887), (-44.097600824, 39.196959086))
            ThreePointArc((-44.097600824, 39.196959086), (-42.426406871, 42.426406871), (-39.196959086, 44.097600824))
            ThreePointArc((-39.196959086, 44.097600824), (-37.063199887, 45.90554666), (-34.846161919, 47.610345509))
            ThreePointArc((-34.846161919, 47.610345509), (-45.254833996, 45.254833996), (-47.610345509, 34.846161919))
        make_face()
        with BuildLine():
            ThreePointArc((-44.569728742, 30.488346624), (-43.406876338, 32.122314465), (-42.184152266, 33.711975581))
            ThreePointArc((-42.184152266, 33.711975581), (-43.848940863, 36.207457539), (-44.097600824, 39.196959086))
            ThreePointArc((-44.097600824, 39.196959086), (-45.90554666, 37.063199887), (-47.610345509, 34.846161919))
            ThreePointArc((-47.610345509, 34.846161919), (-46.384787995, 32.461595157), (-44.569728742, 30.488346624))
        make_face()
        with BuildLine():
            ThreePointArc((-33.711975581, 42.184152266), (-32.122314465, 43.406876338), (-30.488346624, 44.569728742))
            ThreePointArc((-30.488346624, 44.569728742), (-32.461595157, 46.384787995), (-34.846161919, 47.610345509))
            ThreePointArc((-34.846161919, 47.610345509), (-37.063199887, 45.90554666), (-39.196959086, 44.097600824))
            ThreePointArc((-39.196959086, 44.097600824), (-36.207457539, 43.848940863), (-33.711975581, 42.184152266))
        make_face()
        with BuildLine():
            ThreePointArc((-44.569728742, 30.488346624), (-43.406876338, 32.122314465), (-42.184152266, 33.711975581))
            ThreePointArc((-42.184152266, 33.711975581), (-43.848940863, 36.207457539), (-44.097600824, 39.196959086))
            ThreePointArc((-44.097600824, 39.196959086), (-45.90554666, 37.063199887), (-47.610345509, 34.846161919))
            ThreePointArc((-47.610345509, 34.846161919), (-46.384787995, 32.461595157), (-44.569728742, 30.488346624))
        make_face()
        with BuildLine():
            ThreePointArc((-33.711975581, 42.184152266), (-32.122314465, 43.406876338), (-30.488346624, 44.569728742))
            ThreePointArc((-30.488346624, 44.569728742), (-32.461595157, 46.384787995), (-34.846161919, 47.610345509))
            ThreePointArc((-34.846161919, 47.610345509), (-37.063199887, 45.90554666), (-39.196959086, 44.097600824))
            ThreePointArc((-39.196959086, 44.097600824), (-36.207457539, 43.848940863), (-33.711975581, 42.184152266))
        make_face()
    extrude(amount=RAISED_BOSS_H22_4_DEPTH)

    # Sketch1_20 → Raised Boss H10 4 (add)
    with BuildSketch(Plane(origin=(0, 0, 0), x_dir=(1, 0, 0), z_dir=(0, 1, 0))):
        with BuildLine():
            Line((49.595662085, -31.957320012), (94.736257942, -13.578493986))
            Line((94.736257942, -13.578493986), (57.416239001, -13.578493986))
            ThreePointArc((57.416239001, -13.578493986), (54.289336477, -23.101254185), (49.595662085, -31.957320012))
        make_face()
        with BuildLine():
            Line((94.736257942, 13.578493986), (49.595662085, 31.957320012))
            ThreePointArc((49.595662085, 31.957320012), (54.289336477, 23.101254185), (57.416239001, 13.578493986))
            Line((57.416239001, 13.578493986), (94.736257942, 13.578493986))
        make_face()
        with BuildLine():
            Line((-94.736257942, -13.578493986), (-49.595662085, -31.957320012))
            ThreePointArc((-49.595662085, -31.957320012), (-54.289336477, -23.101254185), (-57.416239001, -13.578493986))
            Line((-57.416239001, -13.578493986), (-94.736257942, -13.578493986))
        make_face()
        with BuildLine():
            ThreePointArc((-57.416239001, 13.578493986), (-54.289336477, 23.101254185), (-49.595662085, 31.957320012))
            Line((-49.595662085, 31.957320012), (-94.736257942, 13.578493986))
            Line((-94.736257942, 13.578493986), (-57.416239001, 13.578493986))
        make_face()
    extrude(amount=RAISED_BOSS_H10_4_DEPTH)

    # Sketch1_21 → Raised Boss H12 3 (add)
    # profile 1 of 2: a face of its own
    with BuildSketch(Plane(origin=(0, 0, 0), x_dir=(1, 0, 0), z_dir=(0, 1, 0))):
        with BuildLine():
            ThreePointArc((94.736257942, -13.578493986), (101.416291697, 0), (94.736257942, 13.578493986))
            Line((94.736257942, 13.578493986), (57.416239001, 13.578493986))
            ThreePointArc((57.416239001, 13.578493986), (58.602722211, 6.835272449), (59, 0))
            ThreePointArc((59, 0), (58.602722211, -6.835272449), (57.416239001, -13.578493986))
            Line((57.416239001, -13.578493986), (94.736257942, -13.578493986))
        make_face()
        with Locations(Location((84.275783259, 0, 0), (0, 0, 270))):
            Circle(SKETCH1_21_R, mode=Mode.SUBTRACT)
    # profile 2 of 2: a face of its own
    with BuildSketch(Plane(origin=(0, 0, 0), x_dir=(1, 0, 0), z_dir=(0, 1, 0))):
        with BuildLine():
            Line((-57.416239001, 13.578493986), (-94.736257942, 13.578493986))
            ThreePointArc((-94.736257942, 13.578493986), (-101.416291697, 0), (-94.736257942, -13.578493986))
            Line((-94.736257942, -13.578493986), (-57.416239001, -13.578493986))
            ThreePointArc((-57.416239001, -13.578493986), (-59, 0), (-57.416239001, 13.578493986))
        make_face()
        with Locations(Location((-84.275783259, 0, 0), (0, 0, 270))):
            Circle(SKETCH1_21_R, mode=Mode.SUBTRACT)
    extrude(amount=RAISED_BOSS_H12_3_DEPTH)

    # Boss Cut Sketch → Boss Cut D12 (cut)
    with BuildSketch(Plane(origin=(5, 0, 0), x_dir=(0, 0, -1), z_dir=(1, 0, 0))):
        with Locations((-64.092276099, 13.425612095)):
            Circle(BOSS_CUT_SKETCH_R)
        with Locations((62.815285265, 13.425612095)):
            Circle(BOSS_CUT_SKETCH_R)
    extrude(amount=-BOSS_CUT_D12_DEPTH, mode=Mode.SUBTRACT)


solid = part.part
